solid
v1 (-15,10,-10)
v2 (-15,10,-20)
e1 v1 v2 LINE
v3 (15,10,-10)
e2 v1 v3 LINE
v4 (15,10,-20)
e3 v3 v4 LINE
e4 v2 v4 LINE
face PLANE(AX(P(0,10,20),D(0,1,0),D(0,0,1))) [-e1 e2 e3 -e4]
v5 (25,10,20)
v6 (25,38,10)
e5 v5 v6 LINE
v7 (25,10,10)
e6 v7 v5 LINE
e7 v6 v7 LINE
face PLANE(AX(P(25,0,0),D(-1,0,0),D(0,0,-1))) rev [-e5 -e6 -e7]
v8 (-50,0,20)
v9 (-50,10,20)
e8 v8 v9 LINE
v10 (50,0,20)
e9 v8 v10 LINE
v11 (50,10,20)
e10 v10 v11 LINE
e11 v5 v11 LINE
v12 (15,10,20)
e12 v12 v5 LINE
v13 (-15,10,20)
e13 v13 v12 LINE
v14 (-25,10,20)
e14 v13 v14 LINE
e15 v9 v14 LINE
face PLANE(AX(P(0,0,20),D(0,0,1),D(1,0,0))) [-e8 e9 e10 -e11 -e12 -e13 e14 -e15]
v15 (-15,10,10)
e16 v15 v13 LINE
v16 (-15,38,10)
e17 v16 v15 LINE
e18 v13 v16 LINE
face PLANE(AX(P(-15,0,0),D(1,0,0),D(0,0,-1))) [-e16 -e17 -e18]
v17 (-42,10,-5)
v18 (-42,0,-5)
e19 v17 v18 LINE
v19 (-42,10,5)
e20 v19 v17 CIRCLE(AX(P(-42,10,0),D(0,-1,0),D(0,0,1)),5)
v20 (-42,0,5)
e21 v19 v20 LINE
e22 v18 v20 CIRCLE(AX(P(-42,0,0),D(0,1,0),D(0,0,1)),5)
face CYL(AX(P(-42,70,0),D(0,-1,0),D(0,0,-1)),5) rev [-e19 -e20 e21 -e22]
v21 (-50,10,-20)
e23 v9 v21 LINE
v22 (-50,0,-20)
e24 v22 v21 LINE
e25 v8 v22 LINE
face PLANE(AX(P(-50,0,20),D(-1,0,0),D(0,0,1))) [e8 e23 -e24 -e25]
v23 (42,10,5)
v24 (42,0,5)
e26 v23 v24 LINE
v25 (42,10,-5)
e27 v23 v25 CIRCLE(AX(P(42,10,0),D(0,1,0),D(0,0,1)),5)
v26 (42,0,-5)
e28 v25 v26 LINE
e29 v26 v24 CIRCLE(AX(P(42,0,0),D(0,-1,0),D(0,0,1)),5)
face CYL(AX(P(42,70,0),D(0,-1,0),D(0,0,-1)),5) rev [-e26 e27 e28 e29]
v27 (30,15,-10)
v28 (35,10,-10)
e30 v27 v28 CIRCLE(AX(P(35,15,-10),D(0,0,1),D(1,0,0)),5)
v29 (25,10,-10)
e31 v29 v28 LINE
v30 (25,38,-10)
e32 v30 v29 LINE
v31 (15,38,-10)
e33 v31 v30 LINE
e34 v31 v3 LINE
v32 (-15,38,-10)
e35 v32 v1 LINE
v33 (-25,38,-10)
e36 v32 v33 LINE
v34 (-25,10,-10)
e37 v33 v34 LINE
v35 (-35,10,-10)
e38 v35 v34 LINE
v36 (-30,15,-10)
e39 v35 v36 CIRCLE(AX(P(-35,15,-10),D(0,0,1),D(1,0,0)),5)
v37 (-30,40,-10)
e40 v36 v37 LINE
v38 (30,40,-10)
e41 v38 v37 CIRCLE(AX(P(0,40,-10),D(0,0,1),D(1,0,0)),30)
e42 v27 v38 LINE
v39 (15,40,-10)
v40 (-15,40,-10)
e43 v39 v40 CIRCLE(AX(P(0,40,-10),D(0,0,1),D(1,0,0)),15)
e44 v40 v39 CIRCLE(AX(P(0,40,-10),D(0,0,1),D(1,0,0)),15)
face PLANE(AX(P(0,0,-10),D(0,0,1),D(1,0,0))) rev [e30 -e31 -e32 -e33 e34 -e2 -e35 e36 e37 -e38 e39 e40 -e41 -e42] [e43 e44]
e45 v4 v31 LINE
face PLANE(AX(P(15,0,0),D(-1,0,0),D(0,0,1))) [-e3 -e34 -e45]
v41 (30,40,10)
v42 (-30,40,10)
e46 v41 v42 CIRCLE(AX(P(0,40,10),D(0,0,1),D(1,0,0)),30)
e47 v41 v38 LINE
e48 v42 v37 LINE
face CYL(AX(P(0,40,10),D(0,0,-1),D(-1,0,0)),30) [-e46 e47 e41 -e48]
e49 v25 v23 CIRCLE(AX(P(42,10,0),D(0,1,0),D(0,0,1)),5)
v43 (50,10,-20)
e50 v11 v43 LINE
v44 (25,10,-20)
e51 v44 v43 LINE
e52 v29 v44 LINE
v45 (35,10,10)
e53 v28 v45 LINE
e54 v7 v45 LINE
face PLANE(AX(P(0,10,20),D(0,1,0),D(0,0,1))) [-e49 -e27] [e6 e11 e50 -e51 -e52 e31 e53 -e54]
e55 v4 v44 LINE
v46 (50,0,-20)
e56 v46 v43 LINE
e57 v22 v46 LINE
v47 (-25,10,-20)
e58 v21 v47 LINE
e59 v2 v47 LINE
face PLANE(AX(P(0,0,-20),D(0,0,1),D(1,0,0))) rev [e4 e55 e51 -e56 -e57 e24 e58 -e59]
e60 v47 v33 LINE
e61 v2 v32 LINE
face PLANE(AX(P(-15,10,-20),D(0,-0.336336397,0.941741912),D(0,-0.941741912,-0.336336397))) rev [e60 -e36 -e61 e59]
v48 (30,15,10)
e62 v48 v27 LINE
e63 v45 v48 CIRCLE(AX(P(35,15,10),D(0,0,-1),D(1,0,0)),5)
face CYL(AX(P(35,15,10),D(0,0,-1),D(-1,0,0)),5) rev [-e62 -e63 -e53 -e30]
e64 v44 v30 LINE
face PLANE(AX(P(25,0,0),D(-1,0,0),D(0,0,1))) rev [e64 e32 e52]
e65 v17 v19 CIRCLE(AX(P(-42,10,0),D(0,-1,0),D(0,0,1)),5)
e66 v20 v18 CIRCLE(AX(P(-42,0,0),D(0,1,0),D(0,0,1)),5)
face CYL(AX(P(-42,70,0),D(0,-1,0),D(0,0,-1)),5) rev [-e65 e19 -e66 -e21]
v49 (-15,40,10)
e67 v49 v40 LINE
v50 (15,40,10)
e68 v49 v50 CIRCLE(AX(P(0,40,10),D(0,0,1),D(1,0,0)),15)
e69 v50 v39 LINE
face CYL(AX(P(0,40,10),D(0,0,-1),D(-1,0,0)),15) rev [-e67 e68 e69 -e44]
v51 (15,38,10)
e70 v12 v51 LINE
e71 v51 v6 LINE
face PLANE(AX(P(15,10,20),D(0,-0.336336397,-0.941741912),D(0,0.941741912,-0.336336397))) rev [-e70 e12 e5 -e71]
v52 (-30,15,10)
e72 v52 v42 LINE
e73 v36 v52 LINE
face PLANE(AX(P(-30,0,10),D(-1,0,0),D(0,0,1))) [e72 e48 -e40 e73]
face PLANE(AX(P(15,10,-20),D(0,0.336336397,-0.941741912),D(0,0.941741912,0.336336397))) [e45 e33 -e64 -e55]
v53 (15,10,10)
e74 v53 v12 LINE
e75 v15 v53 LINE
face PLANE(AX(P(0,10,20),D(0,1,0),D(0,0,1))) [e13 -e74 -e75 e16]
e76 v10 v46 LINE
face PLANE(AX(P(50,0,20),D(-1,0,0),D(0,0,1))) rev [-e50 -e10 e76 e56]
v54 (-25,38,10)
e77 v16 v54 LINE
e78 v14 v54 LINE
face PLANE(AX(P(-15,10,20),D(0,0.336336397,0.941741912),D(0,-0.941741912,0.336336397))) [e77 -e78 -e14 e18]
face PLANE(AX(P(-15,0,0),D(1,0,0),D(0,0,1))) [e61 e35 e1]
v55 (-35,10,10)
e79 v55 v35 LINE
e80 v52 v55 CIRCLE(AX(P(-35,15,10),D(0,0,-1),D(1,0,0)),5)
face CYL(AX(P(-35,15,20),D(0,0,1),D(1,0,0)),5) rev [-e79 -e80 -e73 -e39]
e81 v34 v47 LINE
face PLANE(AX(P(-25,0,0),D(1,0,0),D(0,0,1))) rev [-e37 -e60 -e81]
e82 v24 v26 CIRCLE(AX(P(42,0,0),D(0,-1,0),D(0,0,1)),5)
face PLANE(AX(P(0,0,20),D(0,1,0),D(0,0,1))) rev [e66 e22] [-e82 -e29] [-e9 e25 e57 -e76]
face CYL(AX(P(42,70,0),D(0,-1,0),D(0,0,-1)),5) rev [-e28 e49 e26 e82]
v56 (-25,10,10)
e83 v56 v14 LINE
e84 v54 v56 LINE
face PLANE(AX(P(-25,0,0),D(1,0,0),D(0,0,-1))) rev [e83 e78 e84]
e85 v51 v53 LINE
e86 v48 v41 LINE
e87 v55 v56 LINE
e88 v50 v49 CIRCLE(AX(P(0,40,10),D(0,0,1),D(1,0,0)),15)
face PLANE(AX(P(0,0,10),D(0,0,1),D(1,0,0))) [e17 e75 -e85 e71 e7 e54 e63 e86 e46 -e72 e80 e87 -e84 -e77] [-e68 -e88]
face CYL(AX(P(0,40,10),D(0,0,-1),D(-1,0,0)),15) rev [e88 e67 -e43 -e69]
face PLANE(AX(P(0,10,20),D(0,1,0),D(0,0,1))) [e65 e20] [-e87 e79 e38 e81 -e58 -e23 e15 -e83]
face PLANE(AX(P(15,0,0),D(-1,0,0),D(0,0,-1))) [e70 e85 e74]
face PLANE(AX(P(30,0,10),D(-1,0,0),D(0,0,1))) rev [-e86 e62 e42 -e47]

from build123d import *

# Parameters (mm, degrees)
BASE_PLATE_DEPTH                    = 20
SKETCH1_4_R                         = 15
BEARING_HOUSING_DEPTH               = 10
HOUSING_FILLET_R5_A_R               = 5
HOUSING_FILLET_R5_B_R               = 5
SUPPORT_START                       = 25
SUPPORT_RIB_DEPTH                   = 10
RIB_START                           = 25
RIB_MIRROR_FRONT_PLANE_COPY_1_DEPTH = 10
MOUNTING_HOLE_SKETCH_R              = 5
MOUNTING_HOLE_10_DEPTH              = 89.317608663


with BuildPart() as part:
    # Bracket Profile Sketch → Base Plate (new, symmetric)
    with BuildSketch(Plane.XY):
        Polygon((-50, 0), (0, 0), (0, 10), (-30, 10), (-50, 10), align=None)
        Polygon((0, 10), (0, 0), (50, 0), (50, 10), (30, 10), align=None)
    extrude(amount=BASE_PLATE_DEPTH, both=True)

    # Sketch1_4 → Bearing Housing (add, symmetric)
    # profile 1 of 2: a face of its own
    with BuildSketch(Plane.XY):
        Polygon((-50, 10), (-50, 0), (50, 0), (50, 10), (30, 10), (-30, 10), align=None)
    # profile 2 of 2: a face of its own
    with BuildSketch(Plane.XY):
        with BuildLine():
            Line((-30, 40), (-30, 10))
            Line((-30, 10), (30, 10))
            Line((30, 10), (30, 40))
            ThreePointArc((30, 40), (0, 70), (-30, 40))
        make_face()
        with Locations((0, 40)):
            Circle(SKETCH1_4_R, mode=Mode.SUBTRACT)
    extrude(amount=BEARING_HOUSING_DEPTH, both=True)

    # Housing Fillet R5 A
    housing_fillet_r5_a_edges = [part.edges().sort_by_distance(p)[0] for p in [
        (30, 10, 0),
    ]]
    fillet(housing_fillet_r5_a_edges, radius=HOUSING_FILLET_R5_A_R)

    # Housing Fillet R5 B
    housing_fillet_r5_b_edges = [part.edges().sort_by_distance(p)[0] for p in [
        (-30, 10, 0),
    ]]
    fillet(housing_fillet_r5_b_edges, radius=HOUSING_FILLET_R5_B_R)

    # Support Rib Sketch → Support Rib (add)
    with BuildSketch(Plane(origin=(0, 0, 0), x_dir=(0, 0, -1), z_dir=(1, 0, 0)).offset(SUPPORT_START)):
        Polygon((20, 10), (10, 38), (10, 10), align=None)
    support_rib = extrude(amount=-SUPPORT_RIB_DEPTH)

    # Rib Mirror Right Plane: Support Rib across plane
    add(support_rib.mirror(Plane(origin=(0, 0, 0), x_dir=(0, 0, 1), z_dir=(1, 0, 0))))

    # Rib Mirror Front Plane: Support Rib across plane
    add(support_rib.mirror(Plane.XY))

    # Rib Mirror Front Plane copy 1 sketch → Rib Mirror Front Plane copy 1 (add)
    with BuildSketch(Plane.ZY.offset(RIB_START)):
        Polygon((20, 10), (10, 38), (10, 10), align=None)
    extrude(amount=-RIB_MIRROR_FRONT_PLANE_COPY_1_DEPTH)

    # Mounting Hole Sketch → Mounting Hole _10 (cut, through all)
    with BuildSketch(Plane(origin=(0, 0, 0), x_dir=(1, 0, 0), z_dir=(0, 1, 0))):
        with Locations(Location((-42, 0, 0), (0, 0, 270))):
            Circle(MOUNTING_HOLE_SKETCH_R)
    mounting_hole_10 = extrude(amount=MOUNTING_HOLE_10_DEPTH, mode=Mode.SUBTRACT)

    # Mounting Hole Mirror: Mounting Hole _10 across plane
    add(mounting_hole_10.mirror(Plane(origin=(0, 0, 0), x_dir=(0, 0, 1), z_dir=(1, 0, 0))), mode=Mode.SUBTRACT)


solid = part.part
